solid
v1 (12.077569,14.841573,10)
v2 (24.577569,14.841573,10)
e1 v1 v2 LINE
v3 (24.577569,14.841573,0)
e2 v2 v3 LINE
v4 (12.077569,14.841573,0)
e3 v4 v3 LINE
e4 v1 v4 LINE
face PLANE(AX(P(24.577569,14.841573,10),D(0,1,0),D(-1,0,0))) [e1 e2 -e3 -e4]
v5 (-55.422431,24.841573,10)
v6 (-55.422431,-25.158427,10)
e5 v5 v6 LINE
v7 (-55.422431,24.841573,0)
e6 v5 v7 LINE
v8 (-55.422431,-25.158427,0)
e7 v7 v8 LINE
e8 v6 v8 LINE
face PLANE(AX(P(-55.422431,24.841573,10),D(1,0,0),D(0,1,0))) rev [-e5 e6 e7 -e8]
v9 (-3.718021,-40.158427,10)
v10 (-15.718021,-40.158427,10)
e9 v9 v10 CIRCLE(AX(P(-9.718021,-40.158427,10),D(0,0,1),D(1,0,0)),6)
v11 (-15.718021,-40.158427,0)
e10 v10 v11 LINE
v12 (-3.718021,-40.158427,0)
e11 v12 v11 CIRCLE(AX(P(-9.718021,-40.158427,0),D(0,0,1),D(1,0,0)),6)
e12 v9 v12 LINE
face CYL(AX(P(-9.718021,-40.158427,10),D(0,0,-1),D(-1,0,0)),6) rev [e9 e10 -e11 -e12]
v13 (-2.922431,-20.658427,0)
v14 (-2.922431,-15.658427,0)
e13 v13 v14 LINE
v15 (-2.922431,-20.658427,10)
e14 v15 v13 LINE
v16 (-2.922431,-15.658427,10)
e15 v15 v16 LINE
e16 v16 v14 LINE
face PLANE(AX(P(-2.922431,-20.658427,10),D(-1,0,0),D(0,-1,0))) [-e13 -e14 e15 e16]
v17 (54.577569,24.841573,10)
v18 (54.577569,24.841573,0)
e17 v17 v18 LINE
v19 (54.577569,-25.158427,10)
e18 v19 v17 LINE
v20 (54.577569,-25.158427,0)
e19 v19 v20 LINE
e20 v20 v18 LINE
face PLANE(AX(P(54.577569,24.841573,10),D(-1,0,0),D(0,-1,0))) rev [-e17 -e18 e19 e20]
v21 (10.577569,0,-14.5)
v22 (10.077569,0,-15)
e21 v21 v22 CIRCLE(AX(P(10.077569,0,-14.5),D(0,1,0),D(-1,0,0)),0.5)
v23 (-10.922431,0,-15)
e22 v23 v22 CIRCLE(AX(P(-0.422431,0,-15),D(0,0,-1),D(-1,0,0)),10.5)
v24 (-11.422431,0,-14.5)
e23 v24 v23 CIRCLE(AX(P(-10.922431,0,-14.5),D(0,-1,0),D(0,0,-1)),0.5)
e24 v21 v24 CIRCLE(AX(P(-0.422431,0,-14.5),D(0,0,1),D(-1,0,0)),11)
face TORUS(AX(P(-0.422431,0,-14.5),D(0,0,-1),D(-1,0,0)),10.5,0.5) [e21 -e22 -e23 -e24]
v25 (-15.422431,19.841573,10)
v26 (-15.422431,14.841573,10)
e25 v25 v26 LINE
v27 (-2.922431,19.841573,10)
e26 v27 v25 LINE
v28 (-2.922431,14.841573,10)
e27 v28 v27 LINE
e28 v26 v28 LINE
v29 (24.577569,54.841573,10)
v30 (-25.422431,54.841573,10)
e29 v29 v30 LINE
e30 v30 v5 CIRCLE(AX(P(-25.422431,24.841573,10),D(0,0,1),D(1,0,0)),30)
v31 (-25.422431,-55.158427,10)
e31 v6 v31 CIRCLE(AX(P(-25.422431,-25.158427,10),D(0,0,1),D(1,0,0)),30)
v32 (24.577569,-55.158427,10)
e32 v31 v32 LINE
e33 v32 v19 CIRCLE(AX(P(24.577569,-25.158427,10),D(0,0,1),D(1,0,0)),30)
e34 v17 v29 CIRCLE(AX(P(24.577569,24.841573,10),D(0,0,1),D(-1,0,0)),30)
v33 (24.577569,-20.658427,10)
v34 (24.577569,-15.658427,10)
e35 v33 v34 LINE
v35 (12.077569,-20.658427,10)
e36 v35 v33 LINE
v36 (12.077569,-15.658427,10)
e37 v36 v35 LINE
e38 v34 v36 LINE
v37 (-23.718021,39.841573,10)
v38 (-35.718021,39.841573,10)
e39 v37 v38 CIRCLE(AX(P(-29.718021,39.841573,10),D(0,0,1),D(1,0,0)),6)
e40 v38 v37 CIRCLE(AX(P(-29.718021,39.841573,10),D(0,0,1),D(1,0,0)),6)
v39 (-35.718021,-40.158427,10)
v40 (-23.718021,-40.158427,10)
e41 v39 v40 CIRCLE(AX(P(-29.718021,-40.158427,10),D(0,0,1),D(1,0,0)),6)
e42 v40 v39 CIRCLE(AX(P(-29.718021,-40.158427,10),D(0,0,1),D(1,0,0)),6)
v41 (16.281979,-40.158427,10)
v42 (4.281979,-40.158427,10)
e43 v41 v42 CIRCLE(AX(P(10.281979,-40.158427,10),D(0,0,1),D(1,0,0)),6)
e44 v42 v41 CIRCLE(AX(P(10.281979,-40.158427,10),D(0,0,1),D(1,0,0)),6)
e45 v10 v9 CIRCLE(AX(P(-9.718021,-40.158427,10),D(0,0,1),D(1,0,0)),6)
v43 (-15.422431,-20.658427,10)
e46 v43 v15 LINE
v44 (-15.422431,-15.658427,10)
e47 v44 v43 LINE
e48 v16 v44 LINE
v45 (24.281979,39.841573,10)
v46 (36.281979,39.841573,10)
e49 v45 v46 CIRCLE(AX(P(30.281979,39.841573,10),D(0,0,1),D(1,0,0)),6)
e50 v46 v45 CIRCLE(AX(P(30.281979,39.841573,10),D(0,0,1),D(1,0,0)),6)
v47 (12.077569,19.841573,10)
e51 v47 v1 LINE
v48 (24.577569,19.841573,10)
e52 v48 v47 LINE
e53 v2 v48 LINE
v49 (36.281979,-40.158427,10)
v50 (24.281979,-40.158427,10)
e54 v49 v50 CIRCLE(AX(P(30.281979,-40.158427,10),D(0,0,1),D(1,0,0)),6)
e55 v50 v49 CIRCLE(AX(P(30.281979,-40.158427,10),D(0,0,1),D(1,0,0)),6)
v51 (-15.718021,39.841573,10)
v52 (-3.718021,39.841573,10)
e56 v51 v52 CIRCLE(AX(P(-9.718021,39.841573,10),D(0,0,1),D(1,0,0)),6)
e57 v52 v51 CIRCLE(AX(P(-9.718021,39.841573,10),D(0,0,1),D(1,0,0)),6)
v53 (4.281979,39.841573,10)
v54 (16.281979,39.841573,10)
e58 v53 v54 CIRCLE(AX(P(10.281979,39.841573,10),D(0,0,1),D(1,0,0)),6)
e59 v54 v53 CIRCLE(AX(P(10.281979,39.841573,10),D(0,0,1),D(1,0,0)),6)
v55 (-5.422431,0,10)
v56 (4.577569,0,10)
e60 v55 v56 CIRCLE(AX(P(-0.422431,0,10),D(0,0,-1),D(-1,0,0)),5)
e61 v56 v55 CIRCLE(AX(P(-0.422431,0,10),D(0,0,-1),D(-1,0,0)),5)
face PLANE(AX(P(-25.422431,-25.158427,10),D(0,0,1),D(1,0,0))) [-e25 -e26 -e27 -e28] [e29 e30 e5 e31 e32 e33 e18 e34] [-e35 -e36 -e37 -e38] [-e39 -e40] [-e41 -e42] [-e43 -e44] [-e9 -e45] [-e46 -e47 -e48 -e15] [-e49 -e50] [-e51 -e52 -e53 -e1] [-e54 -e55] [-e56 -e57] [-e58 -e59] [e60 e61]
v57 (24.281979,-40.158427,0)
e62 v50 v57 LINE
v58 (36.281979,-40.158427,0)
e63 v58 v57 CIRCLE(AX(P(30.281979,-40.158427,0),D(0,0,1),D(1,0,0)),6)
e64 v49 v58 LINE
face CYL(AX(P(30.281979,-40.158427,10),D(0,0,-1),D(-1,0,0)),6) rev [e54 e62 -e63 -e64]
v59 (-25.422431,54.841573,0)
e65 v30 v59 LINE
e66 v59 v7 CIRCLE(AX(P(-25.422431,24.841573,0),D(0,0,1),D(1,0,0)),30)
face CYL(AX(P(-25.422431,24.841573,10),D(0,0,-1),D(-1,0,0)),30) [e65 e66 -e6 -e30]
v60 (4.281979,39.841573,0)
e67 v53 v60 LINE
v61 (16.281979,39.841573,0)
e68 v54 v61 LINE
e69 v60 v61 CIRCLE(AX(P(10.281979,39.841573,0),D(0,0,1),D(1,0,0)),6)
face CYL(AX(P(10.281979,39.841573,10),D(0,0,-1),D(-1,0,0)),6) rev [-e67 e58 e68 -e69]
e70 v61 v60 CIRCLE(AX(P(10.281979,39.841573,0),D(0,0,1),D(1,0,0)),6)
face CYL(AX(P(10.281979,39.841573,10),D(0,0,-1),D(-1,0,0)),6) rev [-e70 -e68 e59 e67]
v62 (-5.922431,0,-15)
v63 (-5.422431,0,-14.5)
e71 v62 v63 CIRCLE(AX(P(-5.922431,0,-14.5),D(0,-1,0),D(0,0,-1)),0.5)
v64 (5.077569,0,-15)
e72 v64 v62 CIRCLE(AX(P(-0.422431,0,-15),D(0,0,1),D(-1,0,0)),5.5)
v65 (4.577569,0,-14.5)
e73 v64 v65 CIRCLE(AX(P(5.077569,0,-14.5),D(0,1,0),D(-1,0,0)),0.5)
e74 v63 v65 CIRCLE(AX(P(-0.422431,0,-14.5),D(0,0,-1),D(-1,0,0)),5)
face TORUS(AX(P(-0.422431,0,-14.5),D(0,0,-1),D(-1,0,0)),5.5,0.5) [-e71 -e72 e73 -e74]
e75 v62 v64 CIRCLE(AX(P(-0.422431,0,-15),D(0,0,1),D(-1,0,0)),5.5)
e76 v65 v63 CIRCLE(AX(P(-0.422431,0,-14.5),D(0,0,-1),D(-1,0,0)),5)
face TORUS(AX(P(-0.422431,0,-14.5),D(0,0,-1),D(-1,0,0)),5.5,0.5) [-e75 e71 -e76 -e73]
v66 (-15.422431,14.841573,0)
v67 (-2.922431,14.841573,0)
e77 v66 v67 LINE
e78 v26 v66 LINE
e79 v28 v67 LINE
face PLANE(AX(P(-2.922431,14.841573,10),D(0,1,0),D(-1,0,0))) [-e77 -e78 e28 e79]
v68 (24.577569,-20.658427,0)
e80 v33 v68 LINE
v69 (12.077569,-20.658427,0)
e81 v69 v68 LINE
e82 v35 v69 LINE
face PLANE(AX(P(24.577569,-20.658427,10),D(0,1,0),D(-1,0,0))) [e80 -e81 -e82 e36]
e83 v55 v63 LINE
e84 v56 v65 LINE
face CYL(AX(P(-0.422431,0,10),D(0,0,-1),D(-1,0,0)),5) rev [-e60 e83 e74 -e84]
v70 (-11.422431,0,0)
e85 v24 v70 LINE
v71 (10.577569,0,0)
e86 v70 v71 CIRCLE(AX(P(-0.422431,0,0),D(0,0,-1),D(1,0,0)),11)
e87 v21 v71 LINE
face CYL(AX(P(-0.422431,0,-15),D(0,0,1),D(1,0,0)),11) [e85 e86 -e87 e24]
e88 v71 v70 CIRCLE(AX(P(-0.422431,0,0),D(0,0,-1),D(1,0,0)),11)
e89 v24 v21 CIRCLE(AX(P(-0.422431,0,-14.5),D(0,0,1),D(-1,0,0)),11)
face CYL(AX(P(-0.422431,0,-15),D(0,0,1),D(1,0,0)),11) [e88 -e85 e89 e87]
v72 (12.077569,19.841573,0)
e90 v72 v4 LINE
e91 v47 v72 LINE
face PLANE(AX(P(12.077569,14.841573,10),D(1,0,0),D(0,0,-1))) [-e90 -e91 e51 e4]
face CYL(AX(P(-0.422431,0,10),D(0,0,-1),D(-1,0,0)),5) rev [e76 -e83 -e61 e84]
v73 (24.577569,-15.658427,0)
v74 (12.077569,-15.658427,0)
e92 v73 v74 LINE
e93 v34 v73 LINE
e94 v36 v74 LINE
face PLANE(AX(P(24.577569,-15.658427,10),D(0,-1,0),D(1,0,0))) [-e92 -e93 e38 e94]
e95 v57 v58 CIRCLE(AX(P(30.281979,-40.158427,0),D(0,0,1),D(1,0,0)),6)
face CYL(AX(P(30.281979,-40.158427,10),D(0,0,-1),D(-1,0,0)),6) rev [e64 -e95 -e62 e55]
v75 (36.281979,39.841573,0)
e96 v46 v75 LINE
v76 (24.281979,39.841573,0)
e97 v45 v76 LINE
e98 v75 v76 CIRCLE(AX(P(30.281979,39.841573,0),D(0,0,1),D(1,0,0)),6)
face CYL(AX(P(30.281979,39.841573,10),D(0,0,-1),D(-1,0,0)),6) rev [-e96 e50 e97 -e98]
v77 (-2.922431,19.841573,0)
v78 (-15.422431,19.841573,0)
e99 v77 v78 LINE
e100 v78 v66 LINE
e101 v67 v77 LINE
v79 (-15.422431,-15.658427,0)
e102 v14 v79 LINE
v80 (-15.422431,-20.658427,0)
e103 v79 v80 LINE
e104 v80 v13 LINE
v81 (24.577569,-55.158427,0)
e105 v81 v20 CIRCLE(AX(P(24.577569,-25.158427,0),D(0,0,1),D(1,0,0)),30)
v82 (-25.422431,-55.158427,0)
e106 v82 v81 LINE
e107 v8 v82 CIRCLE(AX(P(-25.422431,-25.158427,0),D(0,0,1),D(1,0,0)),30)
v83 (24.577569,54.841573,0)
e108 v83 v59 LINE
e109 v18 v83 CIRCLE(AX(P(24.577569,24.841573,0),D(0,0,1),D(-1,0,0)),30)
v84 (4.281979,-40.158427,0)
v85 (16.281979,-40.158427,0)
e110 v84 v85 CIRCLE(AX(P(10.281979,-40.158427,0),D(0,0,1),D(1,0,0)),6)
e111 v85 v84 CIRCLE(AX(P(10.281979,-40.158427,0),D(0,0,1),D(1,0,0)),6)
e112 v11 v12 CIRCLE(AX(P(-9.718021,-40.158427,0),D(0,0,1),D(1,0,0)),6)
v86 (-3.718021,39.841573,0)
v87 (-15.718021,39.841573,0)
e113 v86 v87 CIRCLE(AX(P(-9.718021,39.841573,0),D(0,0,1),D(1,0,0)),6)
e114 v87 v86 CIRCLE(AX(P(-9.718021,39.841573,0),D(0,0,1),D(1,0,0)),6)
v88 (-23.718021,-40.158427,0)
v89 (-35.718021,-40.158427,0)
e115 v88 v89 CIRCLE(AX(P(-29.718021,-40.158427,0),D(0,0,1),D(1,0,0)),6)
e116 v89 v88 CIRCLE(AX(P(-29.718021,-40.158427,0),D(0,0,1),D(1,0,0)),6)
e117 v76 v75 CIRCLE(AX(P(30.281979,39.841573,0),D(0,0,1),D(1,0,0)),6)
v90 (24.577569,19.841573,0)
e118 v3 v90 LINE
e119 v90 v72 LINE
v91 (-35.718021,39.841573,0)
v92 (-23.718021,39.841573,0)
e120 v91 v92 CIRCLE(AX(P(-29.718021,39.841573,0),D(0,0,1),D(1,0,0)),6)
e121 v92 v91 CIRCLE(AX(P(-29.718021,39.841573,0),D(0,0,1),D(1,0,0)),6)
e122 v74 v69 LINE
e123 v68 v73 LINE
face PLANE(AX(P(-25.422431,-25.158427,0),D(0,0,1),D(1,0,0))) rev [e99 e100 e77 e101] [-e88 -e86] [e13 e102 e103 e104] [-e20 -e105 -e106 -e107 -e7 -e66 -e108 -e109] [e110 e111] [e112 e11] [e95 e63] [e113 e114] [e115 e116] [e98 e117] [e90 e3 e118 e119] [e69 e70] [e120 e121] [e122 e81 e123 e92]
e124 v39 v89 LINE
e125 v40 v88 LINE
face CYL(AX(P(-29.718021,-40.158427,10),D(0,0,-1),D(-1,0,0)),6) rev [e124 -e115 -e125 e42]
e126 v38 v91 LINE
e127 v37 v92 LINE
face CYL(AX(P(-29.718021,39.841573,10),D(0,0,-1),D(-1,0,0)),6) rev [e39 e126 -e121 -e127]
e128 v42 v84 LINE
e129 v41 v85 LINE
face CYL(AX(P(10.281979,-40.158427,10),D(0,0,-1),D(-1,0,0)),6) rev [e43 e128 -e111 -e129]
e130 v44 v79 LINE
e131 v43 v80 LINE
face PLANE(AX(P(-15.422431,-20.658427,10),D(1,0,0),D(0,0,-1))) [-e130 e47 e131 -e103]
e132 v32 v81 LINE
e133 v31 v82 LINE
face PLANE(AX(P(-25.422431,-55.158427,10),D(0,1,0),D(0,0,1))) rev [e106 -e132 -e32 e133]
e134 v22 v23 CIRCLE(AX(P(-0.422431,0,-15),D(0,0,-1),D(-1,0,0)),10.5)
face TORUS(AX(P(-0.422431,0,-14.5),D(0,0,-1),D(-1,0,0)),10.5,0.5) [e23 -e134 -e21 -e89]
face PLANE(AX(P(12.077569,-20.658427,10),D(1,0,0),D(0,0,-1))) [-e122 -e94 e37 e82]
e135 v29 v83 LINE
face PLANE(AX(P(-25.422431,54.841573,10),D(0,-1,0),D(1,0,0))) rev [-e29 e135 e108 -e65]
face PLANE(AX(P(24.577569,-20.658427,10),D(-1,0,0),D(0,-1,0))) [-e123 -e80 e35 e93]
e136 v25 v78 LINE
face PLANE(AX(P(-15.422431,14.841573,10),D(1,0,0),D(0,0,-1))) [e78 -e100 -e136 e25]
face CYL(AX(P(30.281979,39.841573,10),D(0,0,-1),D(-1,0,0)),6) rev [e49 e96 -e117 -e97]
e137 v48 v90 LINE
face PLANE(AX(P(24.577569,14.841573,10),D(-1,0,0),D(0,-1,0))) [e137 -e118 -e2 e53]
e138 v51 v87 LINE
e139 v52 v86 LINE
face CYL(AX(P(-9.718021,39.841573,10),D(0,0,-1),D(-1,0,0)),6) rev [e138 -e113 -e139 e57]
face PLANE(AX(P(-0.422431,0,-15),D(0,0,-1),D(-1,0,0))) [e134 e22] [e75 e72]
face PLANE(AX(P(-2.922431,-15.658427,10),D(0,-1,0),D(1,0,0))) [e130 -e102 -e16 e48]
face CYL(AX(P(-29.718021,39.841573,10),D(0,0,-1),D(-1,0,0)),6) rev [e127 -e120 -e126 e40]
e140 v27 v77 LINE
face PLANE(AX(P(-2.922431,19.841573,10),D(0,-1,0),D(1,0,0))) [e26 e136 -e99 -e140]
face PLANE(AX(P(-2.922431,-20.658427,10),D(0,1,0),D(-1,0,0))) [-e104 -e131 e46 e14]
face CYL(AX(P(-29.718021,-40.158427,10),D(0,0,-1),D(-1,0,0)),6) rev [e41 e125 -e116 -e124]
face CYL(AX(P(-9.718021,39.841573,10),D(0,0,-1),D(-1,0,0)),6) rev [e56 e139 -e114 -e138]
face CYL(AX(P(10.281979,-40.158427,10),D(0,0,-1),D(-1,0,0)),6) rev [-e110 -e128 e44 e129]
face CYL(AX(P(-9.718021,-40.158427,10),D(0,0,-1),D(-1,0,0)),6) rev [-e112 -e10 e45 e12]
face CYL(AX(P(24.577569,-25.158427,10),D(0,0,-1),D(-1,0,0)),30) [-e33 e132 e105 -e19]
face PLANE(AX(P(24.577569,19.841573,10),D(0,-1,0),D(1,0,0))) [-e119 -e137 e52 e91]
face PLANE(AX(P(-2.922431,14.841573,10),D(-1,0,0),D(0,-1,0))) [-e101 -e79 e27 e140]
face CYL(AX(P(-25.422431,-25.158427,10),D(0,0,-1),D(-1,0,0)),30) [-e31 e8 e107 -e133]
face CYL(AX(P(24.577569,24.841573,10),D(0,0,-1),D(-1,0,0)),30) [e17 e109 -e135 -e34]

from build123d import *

# Parameters (mm, degrees)
SKETCH_1_R          = 6
SKETCH_1_W          = 12.5
SKETCH_1_H          = 5
EXTRUDE_1_DEPTH     = 10
SKETCH_2_R          = 11
EXTRUDE_2_DEPTH     = 15
SKETCH_3_R          = 5
CUT_EXTRUDE_1_DEPTH = 25
FILLET_1_R          = 0.5
FILLET_2_R          = 0.5


with BuildPart() as part:
    # 草图1 → 凸台-拉伸1 (new body)
    with BuildSketch(Plane.XY):
        with BuildLine():
            Line((-25.422431237, 54.841573229), (24.577568763, 54.841573229))
            ThreePointArc((24.577568763, 54.841573229), (45.790772199, 46.054776665), (54.577568763, 24.841573229))
            Line((54.577568763, 24.841573229), (54.577568763, -25.158426771))
            ThreePointArc((54.577568763, -25.158426771), (45.790772199, -46.371630206), (24.577568763, -55.158426771))
            Line((24.577568763, -55.158426771), (-25.422431237, -55.158426771))
            ThreePointArc((-25.422431237, -55.158426771), (-46.635634673, -46.371630206), (-55.422431237, -25.158426771))
            Line((-55.422431237, -25.158426771), (-55.422431237, 24.841573229))
            ThreePointArc((-55.422431237, 24.841573229), (-46.635634673, 46.054776665), (-25.422431237, 54.841573229))
        make_face()
        with Locations((-29.718021333, 39.841573229)):
            Circle(SKETCH_1_R, mode=Mode.SUBTRACT)
        with Locations((-9.718021333, 39.841573229)):
            Circle(SKETCH_1_R, mode=Mode.SUBTRACT)
        with Locations((10.281978667, 39.841573229)):
            Circle(SKETCH_1_R, mode=Mode.SUBTRACT)
        with Locations((30.281978667, 39.841573229)):
            Circle(SKETCH_1_R, mode=Mode.SUBTRACT)
        with Locations((30.281978667, -40.158426771)):
            Circle(SKETCH_1_R, mode=Mode.SUBTRACT)
        with Locations((10.281978667, -40.158426771)):
            Circle(SKETCH_1_R, mode=Mode.SUBTRACT)
        with Locations((-9.718021333, -40.158426771)):
            Circle(SKETCH_1_R, mode=Mode.SUBTRACT)
        with Locations((-29.718021333, -40.158426771)):
            Circle(SKETCH_1_R, mode=Mode.SUBTRACT)
        with Locations((18.327568763, 17.341573229)):
            Rectangle(SKETCH_1_W, SKETCH_1_H, mode=Mode.SUBTRACT)
        with Locations((18.327568763, -18.158426771)):
            Rectangle(SKETCH_1_W, SKETCH_1_H, mode=Mode.SUBTRACT)
        with Locations((-9.172431237, -18.158426771)):
            Rectangle(SKETCH_1_W, SKETCH_1_H, mode=Mode.SUBTRACT)
        with Locations((-9.172431237, 17.341573229)):
            Rectangle(SKETCH_1_W, SKETCH_1_H, mode=Mode.SUBTRACT)
    extrude(amount=EXTRUDE_1_DEPTH)

    # 草图2 → 凸台-拉伸2 (add)
    with BuildSketch(Plane(origin=(0, 0, 0), x_dir=(-1, 0, 0), z_dir=(0, 0, -1))):
        with Locations(Location((0.422431237, 0, 0), (0, 0, 180))):
            Circle(SKETCH_2_R)
    extrude(amount=EXTRUDE_2_DEPTH)

    # 草图3 → 切除-拉伸1 (cut)
    with BuildSketch(Plane(origin=(0, 0, -15), x_dir=(-1, 0, 0), z_dir=(0, 0, -1))):
        with Locations((0.422431237, 0)):
            Circle(SKETCH_3_R)
    extrude(amount=-CUT_EXTRUDE_1_DEPTH, mode=Mode.SUBTRACT)

    # 圆角1
    fillet_1_edges = [part.edges().sort_by_distance(p)[0] for p in [
        (4.577568763, 0, -15),
    ]]
    fillet(fillet_1_edges, radius=FILLET_1_R)

    # 圆角2
    fillet_2_edges = [part.edges().sort_by_distance(p)[0] for p in [
        (-11.422431237, 0, -15),
    ]]
    fillet(fillet_2_edges, radius=FILLET_2_R)


solid = part.part
